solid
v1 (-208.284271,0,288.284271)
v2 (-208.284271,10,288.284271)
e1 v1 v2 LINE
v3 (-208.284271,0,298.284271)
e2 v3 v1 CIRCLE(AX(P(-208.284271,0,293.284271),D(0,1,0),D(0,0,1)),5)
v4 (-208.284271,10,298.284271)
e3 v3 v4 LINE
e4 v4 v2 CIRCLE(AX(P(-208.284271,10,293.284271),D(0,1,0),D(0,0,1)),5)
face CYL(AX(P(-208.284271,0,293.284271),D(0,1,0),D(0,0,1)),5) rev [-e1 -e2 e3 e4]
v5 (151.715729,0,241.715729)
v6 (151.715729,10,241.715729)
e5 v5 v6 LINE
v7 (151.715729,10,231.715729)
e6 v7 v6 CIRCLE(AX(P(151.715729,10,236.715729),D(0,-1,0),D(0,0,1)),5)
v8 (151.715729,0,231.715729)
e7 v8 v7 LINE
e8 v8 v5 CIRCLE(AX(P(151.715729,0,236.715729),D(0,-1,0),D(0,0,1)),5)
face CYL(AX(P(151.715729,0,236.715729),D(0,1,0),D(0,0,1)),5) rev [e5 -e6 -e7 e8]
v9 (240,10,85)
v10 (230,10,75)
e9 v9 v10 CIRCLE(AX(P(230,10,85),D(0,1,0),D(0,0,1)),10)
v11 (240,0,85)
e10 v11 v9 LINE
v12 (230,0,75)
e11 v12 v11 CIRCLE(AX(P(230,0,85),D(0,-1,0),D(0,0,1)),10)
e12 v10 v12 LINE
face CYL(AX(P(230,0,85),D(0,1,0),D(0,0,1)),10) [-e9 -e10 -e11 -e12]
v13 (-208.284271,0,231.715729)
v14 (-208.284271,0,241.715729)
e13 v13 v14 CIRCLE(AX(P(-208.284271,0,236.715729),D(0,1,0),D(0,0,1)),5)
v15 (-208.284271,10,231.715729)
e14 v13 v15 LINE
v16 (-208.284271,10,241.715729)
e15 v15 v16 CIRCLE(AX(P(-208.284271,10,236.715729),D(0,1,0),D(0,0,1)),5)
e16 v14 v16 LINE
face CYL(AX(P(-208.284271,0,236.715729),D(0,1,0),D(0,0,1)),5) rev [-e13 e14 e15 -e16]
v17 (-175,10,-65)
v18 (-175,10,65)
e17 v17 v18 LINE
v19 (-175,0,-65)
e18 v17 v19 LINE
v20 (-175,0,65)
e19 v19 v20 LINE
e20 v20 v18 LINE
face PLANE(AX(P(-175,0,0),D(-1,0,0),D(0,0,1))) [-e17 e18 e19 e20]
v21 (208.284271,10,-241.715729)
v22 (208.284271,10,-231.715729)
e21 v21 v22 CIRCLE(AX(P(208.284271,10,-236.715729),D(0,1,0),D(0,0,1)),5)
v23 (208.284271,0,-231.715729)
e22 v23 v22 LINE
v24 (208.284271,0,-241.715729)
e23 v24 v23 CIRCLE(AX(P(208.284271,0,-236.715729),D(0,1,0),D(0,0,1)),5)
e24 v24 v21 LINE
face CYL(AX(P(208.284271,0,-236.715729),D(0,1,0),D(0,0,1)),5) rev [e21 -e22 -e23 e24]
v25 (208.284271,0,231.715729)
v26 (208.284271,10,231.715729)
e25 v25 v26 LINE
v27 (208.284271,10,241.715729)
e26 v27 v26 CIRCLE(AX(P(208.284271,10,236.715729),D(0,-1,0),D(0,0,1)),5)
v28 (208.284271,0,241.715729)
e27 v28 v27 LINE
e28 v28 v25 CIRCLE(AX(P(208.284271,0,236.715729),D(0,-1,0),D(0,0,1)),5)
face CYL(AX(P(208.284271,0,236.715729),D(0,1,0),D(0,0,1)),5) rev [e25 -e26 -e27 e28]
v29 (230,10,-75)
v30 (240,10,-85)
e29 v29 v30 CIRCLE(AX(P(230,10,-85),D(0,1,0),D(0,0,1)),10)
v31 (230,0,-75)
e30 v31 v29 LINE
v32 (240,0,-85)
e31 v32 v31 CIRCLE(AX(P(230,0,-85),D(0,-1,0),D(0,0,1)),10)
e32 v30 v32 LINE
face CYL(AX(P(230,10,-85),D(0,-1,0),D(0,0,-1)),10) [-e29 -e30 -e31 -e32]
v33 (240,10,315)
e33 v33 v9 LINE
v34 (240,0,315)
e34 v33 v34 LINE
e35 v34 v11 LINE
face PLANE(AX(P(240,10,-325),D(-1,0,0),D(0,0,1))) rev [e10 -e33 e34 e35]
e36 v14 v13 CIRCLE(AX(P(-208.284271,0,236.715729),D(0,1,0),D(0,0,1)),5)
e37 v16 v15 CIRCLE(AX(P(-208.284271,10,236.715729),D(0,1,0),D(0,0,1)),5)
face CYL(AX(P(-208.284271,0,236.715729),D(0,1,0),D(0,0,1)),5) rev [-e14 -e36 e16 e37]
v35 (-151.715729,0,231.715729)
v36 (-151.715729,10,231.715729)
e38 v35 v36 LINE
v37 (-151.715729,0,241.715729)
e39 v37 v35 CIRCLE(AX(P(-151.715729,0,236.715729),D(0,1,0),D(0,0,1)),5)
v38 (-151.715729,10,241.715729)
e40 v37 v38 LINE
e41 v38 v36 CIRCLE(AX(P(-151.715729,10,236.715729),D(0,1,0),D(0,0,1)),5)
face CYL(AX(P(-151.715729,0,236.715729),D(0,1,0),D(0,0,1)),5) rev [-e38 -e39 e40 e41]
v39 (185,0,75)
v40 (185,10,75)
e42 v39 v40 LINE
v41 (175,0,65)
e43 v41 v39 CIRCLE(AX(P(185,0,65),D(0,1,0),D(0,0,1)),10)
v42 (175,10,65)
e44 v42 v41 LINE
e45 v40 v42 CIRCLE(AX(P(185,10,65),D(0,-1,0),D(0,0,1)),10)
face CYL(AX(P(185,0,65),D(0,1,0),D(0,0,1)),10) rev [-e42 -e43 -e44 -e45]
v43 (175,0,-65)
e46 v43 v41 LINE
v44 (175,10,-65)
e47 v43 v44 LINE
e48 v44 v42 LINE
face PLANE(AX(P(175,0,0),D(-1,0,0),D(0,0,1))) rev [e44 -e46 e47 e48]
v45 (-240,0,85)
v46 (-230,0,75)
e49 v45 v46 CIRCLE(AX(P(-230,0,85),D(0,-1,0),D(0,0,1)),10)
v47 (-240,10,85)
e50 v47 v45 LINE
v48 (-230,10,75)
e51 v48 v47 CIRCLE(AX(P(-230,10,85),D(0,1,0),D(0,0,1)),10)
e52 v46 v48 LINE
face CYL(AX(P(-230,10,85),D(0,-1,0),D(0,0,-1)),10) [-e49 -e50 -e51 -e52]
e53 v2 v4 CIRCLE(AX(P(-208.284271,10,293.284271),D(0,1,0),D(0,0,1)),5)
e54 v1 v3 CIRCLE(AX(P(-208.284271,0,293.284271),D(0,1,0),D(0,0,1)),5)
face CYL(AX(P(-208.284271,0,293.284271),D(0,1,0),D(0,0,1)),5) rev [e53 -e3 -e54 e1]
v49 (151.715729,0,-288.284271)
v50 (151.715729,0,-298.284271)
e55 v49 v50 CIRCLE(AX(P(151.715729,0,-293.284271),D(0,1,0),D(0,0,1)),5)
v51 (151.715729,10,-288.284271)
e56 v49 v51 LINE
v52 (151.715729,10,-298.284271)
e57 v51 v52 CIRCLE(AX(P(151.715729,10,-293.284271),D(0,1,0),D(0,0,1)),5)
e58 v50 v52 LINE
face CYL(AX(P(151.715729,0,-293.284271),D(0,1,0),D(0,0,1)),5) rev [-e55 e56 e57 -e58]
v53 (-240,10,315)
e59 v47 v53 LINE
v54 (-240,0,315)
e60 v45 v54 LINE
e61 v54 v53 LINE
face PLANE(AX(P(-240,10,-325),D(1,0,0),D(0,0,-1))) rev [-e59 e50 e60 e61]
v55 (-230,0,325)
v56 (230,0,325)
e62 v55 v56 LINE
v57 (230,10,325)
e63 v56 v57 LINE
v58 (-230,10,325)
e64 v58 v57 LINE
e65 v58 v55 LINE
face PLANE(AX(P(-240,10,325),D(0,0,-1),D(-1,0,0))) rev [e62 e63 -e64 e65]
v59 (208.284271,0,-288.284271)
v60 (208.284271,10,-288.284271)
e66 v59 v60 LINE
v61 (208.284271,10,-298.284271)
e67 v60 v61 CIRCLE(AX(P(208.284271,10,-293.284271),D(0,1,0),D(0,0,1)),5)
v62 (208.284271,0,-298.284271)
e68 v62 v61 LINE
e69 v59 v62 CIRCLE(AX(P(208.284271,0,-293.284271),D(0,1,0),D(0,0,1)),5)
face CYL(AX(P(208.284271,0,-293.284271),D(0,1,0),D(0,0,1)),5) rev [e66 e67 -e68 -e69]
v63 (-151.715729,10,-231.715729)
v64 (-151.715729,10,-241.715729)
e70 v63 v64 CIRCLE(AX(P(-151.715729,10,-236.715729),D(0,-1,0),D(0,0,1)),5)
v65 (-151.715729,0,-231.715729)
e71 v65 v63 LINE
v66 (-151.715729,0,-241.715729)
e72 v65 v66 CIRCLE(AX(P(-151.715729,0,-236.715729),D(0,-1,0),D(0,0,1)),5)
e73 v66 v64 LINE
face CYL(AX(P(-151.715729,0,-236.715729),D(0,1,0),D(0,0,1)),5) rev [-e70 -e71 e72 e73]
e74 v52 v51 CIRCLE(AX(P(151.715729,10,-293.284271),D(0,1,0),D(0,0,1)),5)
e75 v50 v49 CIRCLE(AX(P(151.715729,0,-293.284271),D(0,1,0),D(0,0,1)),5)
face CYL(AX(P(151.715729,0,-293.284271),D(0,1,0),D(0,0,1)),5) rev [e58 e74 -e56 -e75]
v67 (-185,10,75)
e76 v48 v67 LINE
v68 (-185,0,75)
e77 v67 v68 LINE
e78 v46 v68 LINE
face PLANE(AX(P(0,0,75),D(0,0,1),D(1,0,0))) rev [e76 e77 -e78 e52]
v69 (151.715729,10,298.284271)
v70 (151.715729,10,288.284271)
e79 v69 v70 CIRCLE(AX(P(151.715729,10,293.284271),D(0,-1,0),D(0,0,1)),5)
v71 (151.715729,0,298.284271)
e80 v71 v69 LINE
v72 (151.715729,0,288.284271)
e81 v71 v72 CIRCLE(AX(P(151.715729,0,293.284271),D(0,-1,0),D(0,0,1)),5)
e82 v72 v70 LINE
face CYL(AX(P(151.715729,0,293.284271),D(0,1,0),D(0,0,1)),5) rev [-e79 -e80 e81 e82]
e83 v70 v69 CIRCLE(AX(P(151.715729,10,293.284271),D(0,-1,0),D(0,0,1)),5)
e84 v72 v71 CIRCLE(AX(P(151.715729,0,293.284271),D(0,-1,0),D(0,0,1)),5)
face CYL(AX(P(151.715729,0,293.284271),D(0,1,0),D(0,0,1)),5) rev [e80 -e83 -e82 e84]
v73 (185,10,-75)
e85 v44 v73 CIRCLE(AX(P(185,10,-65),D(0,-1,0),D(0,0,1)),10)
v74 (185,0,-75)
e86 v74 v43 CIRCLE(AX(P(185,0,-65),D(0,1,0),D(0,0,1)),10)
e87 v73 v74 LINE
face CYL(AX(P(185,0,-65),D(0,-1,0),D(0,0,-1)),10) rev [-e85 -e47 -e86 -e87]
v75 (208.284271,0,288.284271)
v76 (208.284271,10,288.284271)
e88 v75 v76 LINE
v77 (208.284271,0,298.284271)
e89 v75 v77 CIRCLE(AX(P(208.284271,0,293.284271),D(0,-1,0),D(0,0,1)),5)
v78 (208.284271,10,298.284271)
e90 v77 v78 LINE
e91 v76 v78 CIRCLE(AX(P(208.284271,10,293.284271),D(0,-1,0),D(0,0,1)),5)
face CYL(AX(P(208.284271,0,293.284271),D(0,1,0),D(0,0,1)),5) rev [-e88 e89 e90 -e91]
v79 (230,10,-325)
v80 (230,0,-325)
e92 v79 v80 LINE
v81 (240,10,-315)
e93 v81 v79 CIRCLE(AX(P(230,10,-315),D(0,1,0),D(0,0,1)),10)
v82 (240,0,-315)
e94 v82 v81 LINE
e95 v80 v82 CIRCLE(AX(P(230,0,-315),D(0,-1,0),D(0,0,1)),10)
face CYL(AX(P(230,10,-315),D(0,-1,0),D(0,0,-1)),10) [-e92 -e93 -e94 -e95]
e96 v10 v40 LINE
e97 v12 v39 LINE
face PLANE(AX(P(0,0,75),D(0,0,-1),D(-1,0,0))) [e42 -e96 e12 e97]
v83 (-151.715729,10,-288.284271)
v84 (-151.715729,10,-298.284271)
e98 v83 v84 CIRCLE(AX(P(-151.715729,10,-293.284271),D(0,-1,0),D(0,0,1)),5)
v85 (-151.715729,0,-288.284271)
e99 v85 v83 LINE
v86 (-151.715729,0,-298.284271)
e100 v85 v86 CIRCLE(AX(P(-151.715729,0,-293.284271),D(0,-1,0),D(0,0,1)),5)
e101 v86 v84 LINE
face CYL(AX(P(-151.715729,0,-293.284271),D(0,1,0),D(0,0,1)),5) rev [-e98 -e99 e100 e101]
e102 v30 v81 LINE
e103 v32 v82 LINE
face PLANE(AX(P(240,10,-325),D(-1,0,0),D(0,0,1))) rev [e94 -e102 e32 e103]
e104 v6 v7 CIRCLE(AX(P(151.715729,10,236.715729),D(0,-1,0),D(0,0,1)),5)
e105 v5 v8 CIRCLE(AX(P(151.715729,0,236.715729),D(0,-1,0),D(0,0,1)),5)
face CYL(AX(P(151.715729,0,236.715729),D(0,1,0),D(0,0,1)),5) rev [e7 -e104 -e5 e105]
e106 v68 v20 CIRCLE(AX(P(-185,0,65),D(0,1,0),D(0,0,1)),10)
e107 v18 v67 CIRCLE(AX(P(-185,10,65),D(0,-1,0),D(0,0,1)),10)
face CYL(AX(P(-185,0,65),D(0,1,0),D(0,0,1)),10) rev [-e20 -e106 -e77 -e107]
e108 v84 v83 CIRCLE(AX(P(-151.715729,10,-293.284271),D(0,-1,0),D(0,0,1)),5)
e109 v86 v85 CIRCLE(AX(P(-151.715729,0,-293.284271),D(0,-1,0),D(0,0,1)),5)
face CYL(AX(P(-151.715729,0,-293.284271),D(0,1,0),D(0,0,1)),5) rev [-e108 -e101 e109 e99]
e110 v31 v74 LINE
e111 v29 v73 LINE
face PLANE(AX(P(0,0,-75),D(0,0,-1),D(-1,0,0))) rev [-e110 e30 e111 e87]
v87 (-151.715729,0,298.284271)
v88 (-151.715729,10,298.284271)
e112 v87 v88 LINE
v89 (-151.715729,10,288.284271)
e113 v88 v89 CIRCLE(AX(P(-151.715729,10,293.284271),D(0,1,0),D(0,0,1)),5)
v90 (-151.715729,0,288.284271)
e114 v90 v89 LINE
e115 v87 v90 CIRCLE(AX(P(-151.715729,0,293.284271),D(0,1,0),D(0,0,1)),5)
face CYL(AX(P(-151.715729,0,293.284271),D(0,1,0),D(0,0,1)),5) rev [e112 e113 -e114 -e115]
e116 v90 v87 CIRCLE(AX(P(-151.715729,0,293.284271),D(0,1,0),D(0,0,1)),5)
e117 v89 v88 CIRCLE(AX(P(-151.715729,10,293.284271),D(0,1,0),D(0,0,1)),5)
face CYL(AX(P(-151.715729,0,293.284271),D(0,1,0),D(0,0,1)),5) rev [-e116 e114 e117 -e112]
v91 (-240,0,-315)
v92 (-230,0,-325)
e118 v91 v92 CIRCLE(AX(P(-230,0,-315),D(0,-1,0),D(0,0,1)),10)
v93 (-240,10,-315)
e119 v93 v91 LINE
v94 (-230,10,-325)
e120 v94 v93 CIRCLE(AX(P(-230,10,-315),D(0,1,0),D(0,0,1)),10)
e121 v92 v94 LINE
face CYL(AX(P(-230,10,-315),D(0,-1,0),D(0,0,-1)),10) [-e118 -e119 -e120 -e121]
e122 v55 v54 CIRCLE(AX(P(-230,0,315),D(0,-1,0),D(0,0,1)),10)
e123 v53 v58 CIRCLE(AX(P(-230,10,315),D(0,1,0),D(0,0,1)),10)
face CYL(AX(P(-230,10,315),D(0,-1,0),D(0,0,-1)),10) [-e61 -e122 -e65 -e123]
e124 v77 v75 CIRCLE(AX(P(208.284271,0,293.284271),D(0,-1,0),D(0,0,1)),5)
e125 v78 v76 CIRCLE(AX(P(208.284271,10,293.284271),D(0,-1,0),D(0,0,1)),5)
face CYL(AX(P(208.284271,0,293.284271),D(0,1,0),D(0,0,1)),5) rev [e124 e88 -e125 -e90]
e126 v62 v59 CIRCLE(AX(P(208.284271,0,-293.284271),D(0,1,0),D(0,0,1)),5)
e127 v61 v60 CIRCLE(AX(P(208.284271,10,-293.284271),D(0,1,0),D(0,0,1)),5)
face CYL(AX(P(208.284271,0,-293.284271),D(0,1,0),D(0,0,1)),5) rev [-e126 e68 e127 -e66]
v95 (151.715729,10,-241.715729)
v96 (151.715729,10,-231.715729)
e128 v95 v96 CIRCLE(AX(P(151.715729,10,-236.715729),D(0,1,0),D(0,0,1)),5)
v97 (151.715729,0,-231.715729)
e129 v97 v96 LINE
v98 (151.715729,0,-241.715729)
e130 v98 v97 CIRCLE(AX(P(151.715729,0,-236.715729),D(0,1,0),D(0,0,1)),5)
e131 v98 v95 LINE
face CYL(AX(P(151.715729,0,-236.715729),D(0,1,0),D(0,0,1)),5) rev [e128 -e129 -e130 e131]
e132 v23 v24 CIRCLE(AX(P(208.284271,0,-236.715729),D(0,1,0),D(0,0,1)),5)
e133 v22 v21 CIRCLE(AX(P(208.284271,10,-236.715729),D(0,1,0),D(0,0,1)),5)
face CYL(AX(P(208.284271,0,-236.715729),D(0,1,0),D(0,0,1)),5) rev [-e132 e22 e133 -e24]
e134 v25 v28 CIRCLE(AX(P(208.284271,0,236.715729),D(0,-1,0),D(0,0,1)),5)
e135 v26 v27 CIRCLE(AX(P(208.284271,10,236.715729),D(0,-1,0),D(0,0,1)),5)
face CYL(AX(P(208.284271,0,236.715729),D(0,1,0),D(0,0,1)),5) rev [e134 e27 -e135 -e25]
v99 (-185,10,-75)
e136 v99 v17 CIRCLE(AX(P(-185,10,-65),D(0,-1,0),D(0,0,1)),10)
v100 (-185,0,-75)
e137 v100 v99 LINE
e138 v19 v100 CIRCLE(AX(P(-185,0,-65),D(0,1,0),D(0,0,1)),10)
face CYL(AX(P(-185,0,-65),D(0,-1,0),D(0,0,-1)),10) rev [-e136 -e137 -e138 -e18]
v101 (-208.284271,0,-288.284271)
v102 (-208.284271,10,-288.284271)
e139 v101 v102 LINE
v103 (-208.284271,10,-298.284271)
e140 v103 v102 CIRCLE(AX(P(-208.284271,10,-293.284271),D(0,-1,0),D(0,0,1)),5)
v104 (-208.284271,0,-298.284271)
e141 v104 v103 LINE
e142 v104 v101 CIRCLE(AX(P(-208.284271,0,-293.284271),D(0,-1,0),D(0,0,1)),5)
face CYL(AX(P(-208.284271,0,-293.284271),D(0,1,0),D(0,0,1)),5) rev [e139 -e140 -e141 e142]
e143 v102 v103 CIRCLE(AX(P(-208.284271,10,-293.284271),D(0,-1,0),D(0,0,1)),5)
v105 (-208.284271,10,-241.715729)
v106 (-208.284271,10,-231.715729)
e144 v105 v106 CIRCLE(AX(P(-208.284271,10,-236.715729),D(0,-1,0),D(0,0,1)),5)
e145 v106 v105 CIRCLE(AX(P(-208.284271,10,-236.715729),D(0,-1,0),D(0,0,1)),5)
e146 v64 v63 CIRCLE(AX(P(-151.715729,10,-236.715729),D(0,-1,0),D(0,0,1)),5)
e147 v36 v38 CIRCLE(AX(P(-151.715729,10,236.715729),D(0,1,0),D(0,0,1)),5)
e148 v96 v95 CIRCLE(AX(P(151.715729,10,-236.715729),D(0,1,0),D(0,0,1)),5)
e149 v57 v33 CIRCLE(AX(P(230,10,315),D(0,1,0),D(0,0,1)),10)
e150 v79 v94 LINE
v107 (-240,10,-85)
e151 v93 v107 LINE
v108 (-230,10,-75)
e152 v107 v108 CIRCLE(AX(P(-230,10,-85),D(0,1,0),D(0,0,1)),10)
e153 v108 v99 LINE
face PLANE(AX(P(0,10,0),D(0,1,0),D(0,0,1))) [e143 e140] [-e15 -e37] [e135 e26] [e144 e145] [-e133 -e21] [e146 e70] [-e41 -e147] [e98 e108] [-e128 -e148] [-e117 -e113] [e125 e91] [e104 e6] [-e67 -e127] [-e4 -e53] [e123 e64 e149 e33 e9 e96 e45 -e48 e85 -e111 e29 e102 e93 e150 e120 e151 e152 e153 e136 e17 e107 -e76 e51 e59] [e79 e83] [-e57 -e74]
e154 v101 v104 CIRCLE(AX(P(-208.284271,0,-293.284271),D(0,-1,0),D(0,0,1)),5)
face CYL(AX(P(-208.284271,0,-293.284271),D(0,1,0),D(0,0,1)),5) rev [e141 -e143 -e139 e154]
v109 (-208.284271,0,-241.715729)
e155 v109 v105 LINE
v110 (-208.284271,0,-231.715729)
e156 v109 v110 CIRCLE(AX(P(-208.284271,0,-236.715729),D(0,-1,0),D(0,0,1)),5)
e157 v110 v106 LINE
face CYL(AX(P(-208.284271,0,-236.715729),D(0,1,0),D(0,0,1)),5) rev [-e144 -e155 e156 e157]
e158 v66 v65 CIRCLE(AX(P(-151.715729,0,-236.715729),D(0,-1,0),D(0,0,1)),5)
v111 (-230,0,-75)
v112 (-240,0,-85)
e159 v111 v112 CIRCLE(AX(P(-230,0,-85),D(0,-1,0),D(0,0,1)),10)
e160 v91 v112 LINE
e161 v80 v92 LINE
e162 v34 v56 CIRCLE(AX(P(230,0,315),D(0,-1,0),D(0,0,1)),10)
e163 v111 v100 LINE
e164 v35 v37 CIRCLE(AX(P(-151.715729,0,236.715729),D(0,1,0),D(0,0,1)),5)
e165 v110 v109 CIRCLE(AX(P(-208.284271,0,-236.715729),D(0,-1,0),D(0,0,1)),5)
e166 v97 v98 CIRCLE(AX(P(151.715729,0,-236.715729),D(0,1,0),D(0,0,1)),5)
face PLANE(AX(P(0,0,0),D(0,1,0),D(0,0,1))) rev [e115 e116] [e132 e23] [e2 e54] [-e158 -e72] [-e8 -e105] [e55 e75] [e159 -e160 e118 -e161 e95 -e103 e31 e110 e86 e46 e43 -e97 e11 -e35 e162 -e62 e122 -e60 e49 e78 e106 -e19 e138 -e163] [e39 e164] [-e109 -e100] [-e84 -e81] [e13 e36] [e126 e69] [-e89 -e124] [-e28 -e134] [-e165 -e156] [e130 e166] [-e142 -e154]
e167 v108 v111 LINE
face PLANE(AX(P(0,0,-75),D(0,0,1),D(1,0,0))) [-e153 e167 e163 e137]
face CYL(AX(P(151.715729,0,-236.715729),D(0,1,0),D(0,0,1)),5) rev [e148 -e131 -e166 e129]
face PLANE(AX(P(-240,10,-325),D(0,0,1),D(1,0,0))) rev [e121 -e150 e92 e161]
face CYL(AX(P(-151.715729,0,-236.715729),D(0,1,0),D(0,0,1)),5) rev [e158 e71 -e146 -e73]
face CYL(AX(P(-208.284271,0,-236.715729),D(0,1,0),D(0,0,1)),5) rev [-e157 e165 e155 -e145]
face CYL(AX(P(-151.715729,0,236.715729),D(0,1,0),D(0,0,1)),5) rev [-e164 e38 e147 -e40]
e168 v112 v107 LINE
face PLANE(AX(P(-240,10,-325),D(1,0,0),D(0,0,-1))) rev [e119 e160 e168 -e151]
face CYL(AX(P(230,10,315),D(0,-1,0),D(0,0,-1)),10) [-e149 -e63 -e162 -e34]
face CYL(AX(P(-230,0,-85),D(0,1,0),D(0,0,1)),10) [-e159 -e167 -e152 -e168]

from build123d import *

# Parameters (mm, degrees)
SKETCH1_W           = 480
SKETCH1_H           = 650
BOSS_EXTRUDE1_DEPTH = 10
SKETCH3_W           = 130
SKETCH3_H           = 150
CUT_EXTRUDE1_DEPTH  = 10
FILLET1_R           = 10
FILLET3_R           = 10
SKETCH5_R           = 5
CUT_EXTRUDE2_DEPTH  = 10


with BuildPart() as part:
    # Sketch1 → Boss-Extrude1 (new body)
    with BuildSketch(Plane(origin=(0, 0, 0), x_dir=(1, 0, 0), z_dir=(0, 1, 0))):
        Rectangle(SKETCH1_W, SKETCH1_H)
    extrude(amount=BOSS_EXTRUDE1_DEPTH)

    # Sketch3 → Cut-Extrude1 (cut)
    with BuildSketch(Plane(origin=(0, 10, 0), x_dir=(1, 0, 0), z_dir=(0, 1, 0))):
        with Locations((240, 0)):
            Rectangle(SKETCH3_W, SKETCH3_H)
        with Locations((-240, 0)):
            Rectangle(SKETCH3_W, SKETCH3_H)
    extrude(amount=-CUT_EXTRUDE1_DEPTH, mode=Mode.SUBTRACT)

    # Fillet1
    fillet1_edges = [part.edges().sort_by_distance(p)[0] for p in [
        (240, 5, -75),
        (175, 5, -75),
        (240, 5, 75),
        (175, 5, 75),
        (-240, 5, 75),
        (-175, 5, 75),
        (-175, 5, -75),
        (-240, 5, -75),
    ]]
    fillet(fillet1_edges, radius=FILLET1_R)

    # Fillet3
    fillet3_edges = [part.edges().sort_by_distance(p)[0] for p in [
        (240, 5, 325),
        (-240, 5, 325),
        (-240, 5, -325),
        (240, 5, -325),
    ]]
    fillet(fillet3_edges, radius=FILLET3_R)

    # Sketch5 → Cut-Extrude2 (cut)
    with BuildSketch(Plane(origin=(0, 10, 0), x_dir=(1, 0, 0), z_dir=(0, 1, 0))):
        with Locations(Location((-208.284271247, -293.284271247, 0), (0, 0, 270))):
            Circle(SKETCH5_R)
        with Locations(Location((-208.284271247, -236.715728753, 0), (0, 0, 270))):
            Circle(SKETCH5_R)
        with Locations(Location((-151.715728753, -236.715728753, 0), (0, 0, 270))):
            Circle(SKETCH5_R)
        with Locations(Location((-151.715728753, -293.284271247, 0), (0, 0, 270))):
            Circle(SKETCH5_R)
        with Locations(Location((208.284271247, -293.284271247, 0), (0, 0, 270))):
            Circle(SKETCH5_R)
        with Locations(Location((151.715728753, -293.284271247, 0), (0, 0, 270))):
            Circle(SKETCH5_R)
        with Locations(Location((151.715728753, -236.715728753, 0), (0, 0, 270))):
            Circle(SKETCH5_R)
        with Locations(Location((208.284271247, -236.715728753, 0), (0, 0, 270))):
            Circle(SKETCH5_R)
        with Locations(Location((-208.284271247, 236.715728753, 0), (0, 0, 270))):
            Circle(SKETCH5_R)
        with Locations(Location((208.284271247, 293.284271247, 0), (0, 0, 270))):
            Circle(SKETCH5_R)
        with Locations(Location((208.284271247, 236.715728753, 0), (0, 0, 270))):
            Circle(SKETCH5_R)
        with Locations(Location((151.715728753, 293.284271247, 0), (0, 0, 270))):
            Circle(SKETCH5_R)
        with Locations(Location((151.715728753, 236.715728753, 0), (0, 0, 270))):
            Circle(SKETCH5_R)
        with Locations(Location((-151.715728753, 293.284271247, 0), (0, 0, 270))):
            Circle(SKETCH5_R)
        with Locations(Location((-208.284271247, 293.284271247, 0), (0, 0, 270))):
            Circle(SKETCH5_R)
        with Locations(Location((-151.715728753, 236.715728753, 0), (0, 0, 270))):
            Circle(SKETCH5_R)
    extrude(amount=-CUT_EXTRUDE2_DEPTH, mode=Mode.SUBTRACT)


solid = part.part
